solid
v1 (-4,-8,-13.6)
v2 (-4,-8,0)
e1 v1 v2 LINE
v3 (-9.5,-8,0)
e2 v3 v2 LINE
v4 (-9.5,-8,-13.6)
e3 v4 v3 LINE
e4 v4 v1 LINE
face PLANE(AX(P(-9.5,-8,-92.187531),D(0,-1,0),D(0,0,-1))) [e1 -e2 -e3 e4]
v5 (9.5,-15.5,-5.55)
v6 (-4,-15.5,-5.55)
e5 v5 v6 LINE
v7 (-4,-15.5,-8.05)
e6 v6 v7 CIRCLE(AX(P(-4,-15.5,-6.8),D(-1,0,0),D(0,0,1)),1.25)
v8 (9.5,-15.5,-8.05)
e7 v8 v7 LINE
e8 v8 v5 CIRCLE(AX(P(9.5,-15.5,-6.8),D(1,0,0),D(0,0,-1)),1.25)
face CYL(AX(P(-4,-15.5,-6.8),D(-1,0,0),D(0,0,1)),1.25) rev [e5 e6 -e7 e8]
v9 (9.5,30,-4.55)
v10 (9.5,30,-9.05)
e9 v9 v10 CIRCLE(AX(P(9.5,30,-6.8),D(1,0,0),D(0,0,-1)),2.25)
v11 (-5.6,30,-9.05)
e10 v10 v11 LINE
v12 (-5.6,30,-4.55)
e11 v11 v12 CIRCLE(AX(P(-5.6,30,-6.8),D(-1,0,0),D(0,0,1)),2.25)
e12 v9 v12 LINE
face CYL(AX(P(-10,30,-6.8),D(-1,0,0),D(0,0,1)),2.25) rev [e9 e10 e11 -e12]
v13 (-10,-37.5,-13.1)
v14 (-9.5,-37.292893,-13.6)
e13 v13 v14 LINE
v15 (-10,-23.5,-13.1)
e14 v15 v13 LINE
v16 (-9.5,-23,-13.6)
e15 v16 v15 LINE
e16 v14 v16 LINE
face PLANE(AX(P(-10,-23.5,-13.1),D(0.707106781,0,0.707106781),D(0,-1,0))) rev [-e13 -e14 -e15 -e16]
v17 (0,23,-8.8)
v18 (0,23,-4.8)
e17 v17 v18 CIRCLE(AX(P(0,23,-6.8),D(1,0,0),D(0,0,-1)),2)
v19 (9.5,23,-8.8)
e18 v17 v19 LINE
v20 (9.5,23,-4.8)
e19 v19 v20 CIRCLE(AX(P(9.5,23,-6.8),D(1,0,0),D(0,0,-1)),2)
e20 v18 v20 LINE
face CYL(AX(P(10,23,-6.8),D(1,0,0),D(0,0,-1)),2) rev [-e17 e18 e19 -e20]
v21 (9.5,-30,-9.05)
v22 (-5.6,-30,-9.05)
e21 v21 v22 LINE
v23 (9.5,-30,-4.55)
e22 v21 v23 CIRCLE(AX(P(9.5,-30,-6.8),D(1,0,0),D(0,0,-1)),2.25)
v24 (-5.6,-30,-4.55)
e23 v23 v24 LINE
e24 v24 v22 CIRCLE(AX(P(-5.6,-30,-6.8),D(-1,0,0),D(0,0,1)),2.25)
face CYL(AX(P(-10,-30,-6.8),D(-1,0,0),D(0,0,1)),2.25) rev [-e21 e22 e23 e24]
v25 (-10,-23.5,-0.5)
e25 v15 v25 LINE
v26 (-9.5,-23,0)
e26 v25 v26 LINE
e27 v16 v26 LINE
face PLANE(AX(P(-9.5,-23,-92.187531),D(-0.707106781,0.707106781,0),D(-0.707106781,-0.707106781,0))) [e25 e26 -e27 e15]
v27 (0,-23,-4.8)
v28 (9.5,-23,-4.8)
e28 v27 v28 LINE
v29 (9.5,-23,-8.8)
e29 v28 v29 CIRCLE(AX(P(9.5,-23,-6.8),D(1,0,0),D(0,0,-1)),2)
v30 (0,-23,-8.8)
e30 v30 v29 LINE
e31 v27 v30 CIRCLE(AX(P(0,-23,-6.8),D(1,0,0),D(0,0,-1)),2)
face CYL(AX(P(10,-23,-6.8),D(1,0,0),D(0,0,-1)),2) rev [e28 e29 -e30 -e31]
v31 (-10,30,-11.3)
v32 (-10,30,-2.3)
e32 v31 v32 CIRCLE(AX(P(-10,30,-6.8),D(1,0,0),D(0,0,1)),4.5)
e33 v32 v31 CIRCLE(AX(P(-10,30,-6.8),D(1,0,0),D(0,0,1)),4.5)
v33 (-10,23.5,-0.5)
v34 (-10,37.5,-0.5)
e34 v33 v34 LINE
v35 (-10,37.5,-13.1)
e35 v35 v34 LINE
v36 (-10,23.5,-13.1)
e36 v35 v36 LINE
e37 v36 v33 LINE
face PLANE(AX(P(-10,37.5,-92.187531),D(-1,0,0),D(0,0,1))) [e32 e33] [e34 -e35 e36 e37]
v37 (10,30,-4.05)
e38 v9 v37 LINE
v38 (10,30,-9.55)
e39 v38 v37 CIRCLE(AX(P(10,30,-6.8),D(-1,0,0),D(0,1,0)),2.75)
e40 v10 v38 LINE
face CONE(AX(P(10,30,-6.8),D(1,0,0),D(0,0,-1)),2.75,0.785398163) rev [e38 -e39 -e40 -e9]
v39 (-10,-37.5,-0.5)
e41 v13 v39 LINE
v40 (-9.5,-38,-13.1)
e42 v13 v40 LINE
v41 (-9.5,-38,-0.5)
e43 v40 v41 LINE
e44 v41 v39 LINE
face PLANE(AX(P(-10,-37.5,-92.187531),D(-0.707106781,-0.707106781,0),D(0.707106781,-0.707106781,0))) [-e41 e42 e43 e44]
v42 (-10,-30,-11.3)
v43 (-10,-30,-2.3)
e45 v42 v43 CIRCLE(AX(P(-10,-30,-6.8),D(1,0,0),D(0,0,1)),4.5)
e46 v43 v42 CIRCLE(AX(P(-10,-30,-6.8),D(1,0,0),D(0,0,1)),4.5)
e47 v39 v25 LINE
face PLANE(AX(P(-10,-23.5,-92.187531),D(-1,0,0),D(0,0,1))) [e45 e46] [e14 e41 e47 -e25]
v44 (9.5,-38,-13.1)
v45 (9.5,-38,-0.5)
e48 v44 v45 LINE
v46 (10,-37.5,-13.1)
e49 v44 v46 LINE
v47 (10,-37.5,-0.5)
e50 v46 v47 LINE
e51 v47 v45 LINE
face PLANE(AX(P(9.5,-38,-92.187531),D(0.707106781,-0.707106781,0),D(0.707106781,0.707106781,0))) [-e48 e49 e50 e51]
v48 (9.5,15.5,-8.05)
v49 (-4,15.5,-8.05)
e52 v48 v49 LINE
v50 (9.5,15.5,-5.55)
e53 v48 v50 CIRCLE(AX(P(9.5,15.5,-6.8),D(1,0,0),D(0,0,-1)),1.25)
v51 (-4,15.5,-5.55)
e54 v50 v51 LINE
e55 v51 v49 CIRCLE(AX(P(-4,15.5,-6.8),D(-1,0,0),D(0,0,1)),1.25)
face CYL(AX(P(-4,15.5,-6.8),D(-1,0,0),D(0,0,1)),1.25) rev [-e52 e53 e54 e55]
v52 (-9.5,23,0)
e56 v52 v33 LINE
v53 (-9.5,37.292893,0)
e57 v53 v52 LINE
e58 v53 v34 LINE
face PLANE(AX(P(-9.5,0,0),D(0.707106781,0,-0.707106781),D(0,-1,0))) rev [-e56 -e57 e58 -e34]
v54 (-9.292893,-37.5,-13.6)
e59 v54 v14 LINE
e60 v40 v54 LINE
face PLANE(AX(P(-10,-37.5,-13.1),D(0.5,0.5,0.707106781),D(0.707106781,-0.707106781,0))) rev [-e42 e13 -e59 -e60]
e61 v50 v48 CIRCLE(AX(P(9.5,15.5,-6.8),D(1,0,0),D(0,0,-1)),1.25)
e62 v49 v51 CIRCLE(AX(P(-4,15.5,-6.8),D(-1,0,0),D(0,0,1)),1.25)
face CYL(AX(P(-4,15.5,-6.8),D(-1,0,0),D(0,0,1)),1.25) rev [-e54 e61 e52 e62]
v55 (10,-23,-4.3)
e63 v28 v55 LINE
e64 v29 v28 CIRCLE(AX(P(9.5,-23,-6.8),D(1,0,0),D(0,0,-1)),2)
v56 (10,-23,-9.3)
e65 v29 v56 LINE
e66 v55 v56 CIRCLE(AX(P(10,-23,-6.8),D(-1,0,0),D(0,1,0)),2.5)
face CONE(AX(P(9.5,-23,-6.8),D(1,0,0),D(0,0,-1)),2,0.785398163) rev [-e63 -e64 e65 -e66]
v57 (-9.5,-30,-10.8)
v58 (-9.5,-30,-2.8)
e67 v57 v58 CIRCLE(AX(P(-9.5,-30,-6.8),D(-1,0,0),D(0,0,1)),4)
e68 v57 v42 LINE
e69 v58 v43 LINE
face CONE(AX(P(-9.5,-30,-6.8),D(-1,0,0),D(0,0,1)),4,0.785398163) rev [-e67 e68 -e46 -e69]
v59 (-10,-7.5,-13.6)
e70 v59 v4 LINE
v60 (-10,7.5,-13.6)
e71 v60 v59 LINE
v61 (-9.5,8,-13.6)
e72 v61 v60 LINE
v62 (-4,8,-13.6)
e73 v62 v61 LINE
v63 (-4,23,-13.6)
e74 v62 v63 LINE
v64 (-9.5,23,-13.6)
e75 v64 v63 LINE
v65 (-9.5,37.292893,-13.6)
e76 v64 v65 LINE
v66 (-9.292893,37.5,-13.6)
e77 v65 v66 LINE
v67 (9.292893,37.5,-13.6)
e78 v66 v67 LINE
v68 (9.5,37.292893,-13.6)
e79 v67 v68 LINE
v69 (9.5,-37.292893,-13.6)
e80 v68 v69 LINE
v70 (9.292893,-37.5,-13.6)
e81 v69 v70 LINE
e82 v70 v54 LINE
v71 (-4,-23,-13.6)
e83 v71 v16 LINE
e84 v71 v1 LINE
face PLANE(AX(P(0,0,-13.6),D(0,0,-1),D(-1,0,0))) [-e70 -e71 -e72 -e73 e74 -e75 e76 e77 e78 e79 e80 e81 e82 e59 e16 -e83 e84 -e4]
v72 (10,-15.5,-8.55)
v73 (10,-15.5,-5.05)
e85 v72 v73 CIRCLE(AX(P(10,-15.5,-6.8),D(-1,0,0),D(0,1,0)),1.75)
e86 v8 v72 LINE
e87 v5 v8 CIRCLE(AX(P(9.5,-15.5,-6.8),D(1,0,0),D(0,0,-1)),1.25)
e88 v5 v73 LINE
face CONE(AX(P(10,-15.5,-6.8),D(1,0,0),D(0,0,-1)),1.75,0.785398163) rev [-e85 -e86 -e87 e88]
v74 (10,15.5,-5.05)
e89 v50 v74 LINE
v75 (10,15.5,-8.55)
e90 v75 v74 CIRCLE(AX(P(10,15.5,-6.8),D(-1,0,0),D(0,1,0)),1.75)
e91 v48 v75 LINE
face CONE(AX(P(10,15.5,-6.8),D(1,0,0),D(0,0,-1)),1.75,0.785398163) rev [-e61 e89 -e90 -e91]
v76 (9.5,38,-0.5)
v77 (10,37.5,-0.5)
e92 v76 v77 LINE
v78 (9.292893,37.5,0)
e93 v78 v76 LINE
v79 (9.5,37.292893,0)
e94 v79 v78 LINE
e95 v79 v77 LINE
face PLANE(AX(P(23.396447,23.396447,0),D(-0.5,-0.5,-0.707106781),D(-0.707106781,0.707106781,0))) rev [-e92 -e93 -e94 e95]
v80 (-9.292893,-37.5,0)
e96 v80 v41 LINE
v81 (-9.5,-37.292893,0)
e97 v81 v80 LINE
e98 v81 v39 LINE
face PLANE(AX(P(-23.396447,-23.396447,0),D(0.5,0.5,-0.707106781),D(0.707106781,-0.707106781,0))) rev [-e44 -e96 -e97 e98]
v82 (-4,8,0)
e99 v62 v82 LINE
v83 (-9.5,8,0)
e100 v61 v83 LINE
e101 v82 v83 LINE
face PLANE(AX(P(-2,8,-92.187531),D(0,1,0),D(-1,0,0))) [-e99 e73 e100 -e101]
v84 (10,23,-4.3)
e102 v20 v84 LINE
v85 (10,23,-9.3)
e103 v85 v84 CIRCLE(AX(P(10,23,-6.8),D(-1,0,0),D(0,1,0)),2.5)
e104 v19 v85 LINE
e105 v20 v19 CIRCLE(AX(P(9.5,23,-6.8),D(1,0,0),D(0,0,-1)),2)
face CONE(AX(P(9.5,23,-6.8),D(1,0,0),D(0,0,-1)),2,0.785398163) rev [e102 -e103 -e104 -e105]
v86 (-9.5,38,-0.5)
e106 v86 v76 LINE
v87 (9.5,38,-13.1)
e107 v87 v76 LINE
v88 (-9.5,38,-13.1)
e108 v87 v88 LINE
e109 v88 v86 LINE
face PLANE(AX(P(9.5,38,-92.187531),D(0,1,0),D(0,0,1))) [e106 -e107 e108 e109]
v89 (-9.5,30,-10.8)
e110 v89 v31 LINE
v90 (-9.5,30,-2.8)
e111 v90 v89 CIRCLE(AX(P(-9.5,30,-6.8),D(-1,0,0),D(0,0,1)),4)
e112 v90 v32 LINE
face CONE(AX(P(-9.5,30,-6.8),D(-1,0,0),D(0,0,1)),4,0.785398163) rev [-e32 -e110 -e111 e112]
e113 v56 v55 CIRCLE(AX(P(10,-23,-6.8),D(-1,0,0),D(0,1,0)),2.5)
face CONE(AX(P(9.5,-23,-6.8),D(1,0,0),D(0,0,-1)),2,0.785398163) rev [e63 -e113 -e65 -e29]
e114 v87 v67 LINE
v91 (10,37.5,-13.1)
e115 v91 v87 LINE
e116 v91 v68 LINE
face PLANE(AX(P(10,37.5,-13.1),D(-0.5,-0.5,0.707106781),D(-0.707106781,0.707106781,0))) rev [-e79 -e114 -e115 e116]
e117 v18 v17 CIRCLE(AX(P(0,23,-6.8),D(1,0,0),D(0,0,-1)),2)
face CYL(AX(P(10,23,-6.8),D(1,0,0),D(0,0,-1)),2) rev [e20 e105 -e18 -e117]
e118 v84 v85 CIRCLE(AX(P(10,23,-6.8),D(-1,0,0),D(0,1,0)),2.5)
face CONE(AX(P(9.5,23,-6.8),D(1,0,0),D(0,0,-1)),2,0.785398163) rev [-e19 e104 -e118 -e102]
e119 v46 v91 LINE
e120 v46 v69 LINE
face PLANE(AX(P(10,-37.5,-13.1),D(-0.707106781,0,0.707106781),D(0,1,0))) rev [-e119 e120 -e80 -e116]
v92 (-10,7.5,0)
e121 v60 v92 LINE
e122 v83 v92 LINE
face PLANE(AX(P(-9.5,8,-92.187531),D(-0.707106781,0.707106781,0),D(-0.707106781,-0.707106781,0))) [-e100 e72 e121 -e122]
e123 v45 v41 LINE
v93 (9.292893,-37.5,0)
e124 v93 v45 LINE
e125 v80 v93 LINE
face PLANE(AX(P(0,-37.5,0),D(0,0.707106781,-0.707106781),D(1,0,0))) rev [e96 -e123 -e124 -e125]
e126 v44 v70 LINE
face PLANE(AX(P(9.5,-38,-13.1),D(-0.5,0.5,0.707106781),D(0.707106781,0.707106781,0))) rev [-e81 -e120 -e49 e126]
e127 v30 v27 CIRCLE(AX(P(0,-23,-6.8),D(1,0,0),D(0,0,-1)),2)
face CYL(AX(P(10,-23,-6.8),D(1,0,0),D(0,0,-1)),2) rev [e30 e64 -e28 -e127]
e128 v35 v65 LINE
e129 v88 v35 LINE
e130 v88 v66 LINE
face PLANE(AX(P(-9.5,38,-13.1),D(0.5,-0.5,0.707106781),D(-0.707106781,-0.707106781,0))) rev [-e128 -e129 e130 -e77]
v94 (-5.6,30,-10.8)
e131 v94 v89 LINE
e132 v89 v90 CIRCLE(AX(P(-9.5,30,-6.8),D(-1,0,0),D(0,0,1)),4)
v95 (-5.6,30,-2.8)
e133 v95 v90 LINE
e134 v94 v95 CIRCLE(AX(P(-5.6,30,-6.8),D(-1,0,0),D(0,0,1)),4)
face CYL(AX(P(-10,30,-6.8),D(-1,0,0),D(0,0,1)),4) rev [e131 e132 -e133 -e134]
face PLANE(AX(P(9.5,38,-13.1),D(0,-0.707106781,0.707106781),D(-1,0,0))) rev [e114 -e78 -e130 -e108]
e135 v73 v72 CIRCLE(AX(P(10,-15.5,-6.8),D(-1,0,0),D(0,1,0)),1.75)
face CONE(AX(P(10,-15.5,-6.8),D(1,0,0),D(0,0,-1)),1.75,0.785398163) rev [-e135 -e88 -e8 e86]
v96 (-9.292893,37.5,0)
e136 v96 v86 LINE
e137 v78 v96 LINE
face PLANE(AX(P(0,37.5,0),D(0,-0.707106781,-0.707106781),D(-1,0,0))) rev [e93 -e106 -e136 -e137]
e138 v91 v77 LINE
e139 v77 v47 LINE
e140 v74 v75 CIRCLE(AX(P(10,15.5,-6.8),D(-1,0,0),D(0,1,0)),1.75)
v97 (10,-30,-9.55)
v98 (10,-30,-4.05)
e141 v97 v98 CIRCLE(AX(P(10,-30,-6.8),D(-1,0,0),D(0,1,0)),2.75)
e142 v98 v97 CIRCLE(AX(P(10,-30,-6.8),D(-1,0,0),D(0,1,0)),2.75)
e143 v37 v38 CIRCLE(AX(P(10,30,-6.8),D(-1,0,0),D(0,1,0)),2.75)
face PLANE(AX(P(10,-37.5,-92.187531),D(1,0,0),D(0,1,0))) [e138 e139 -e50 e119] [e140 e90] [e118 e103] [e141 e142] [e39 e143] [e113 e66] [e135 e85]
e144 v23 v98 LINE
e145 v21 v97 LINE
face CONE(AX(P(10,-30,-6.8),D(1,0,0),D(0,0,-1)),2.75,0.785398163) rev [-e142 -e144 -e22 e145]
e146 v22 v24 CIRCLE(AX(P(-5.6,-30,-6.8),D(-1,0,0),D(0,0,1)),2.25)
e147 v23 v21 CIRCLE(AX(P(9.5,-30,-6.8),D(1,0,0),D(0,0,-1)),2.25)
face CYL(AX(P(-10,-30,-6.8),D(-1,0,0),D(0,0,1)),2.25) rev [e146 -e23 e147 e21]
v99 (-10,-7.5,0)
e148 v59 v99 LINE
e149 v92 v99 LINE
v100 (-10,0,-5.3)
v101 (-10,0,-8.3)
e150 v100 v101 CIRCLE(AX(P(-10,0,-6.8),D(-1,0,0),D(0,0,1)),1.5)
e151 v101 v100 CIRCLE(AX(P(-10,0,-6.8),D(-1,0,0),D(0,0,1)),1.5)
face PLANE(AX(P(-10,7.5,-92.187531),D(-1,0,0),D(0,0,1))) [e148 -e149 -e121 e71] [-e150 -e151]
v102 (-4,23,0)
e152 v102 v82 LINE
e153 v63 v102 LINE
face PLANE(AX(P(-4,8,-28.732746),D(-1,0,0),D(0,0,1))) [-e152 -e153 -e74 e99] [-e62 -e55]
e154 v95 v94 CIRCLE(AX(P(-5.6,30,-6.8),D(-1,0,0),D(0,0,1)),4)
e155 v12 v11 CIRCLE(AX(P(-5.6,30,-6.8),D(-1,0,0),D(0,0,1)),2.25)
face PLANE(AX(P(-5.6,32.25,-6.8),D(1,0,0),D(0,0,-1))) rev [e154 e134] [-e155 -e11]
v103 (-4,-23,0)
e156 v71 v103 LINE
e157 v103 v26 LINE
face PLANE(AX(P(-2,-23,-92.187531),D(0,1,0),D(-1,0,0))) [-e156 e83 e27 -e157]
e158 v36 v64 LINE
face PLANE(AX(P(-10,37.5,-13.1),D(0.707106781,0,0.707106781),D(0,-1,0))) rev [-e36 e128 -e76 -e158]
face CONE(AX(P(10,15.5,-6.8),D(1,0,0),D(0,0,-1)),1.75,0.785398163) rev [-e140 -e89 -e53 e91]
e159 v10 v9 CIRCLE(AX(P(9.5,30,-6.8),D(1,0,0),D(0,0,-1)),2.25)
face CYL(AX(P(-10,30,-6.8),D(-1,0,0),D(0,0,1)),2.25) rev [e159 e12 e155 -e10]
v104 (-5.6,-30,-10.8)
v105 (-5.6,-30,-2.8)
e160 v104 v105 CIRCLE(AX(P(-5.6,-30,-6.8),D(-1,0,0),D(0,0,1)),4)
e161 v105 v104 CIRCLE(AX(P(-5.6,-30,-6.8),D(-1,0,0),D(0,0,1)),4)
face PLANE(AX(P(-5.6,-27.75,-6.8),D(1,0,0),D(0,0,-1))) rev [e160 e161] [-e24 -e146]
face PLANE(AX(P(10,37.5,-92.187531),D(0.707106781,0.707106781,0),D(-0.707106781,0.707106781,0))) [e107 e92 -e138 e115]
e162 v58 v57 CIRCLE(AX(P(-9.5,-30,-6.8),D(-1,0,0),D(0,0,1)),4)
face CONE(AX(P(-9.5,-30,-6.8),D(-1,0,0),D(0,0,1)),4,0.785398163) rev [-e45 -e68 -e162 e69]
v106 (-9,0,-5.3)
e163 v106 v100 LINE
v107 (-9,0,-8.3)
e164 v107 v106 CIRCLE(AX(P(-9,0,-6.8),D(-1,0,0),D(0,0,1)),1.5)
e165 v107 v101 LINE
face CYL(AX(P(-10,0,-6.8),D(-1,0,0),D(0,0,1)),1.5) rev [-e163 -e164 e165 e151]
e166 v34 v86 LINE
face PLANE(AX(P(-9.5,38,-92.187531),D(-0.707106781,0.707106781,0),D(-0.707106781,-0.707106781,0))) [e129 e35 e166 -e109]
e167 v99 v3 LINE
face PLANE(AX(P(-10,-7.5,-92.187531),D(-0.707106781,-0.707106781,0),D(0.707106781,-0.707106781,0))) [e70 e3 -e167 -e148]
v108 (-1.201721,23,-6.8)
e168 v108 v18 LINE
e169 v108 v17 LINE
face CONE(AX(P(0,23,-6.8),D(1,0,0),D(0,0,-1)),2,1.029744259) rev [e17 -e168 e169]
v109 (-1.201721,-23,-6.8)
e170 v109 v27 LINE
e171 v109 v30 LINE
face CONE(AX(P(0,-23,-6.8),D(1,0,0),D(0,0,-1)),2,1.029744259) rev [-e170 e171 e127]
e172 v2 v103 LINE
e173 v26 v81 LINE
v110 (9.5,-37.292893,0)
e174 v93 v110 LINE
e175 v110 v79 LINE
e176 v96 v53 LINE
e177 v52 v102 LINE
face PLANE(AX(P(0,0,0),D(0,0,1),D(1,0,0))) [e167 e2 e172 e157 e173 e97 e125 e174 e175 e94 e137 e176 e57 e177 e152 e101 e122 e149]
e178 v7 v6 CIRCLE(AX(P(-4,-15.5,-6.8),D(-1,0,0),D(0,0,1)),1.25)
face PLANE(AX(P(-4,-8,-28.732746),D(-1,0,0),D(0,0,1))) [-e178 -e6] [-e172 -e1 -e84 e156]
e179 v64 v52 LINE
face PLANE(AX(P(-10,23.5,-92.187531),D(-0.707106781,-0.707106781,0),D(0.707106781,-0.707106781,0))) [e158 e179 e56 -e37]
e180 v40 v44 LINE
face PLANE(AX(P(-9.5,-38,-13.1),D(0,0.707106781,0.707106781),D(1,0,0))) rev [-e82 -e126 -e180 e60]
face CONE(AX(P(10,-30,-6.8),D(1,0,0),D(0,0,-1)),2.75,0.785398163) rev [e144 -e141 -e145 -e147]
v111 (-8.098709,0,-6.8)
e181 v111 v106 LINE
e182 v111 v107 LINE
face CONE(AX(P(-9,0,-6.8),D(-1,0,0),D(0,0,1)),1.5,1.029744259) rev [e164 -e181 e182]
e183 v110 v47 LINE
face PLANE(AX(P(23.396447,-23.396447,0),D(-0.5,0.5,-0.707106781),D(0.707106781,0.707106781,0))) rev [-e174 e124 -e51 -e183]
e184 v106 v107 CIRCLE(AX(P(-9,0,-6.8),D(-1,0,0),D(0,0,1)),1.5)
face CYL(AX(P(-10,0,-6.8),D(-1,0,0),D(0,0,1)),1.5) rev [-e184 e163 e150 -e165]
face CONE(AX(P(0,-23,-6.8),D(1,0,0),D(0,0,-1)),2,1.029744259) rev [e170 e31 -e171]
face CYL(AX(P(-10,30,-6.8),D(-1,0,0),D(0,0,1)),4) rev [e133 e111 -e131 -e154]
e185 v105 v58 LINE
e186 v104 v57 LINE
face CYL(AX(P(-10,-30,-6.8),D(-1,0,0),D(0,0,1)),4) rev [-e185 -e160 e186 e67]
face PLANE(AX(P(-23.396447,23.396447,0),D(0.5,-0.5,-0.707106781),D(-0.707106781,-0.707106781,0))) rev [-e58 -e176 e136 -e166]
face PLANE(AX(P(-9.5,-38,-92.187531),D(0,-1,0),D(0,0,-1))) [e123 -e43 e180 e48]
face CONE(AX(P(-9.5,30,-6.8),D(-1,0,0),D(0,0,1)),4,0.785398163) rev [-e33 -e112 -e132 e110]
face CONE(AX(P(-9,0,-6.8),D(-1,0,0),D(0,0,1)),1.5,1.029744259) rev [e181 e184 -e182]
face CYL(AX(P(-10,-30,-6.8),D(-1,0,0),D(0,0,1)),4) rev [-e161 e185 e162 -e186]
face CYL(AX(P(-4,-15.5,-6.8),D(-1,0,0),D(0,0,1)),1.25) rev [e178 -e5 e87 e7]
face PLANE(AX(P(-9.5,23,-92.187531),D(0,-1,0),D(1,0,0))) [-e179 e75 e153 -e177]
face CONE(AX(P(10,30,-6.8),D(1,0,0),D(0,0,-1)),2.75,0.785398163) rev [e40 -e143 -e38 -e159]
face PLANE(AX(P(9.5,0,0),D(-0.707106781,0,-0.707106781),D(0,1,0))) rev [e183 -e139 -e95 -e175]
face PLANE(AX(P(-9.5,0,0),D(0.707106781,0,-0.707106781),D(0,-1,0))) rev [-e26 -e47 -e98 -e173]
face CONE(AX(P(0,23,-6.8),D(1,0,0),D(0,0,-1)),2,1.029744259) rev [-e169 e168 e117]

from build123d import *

# Parameters (mm, degrees)
EXTRUDE_1_DEPTH              = 13.6
CHAMFER_1_SIZE               = 0.5
HOLE_WIZARD_M4_1_D           = 4.5
HOLE_WIZARD_M4_1_CBORE_D     = 8
HOLE_WIZARD_M4_1_CBORE_DEPTH = 4.4
SKETCH_6_W                   = 2
SKETCH_6_H                   = 15
EXTRUDE_2_DEPTH              = 13.6
HOLE_WIZARD_M3_1_D           = 2.5
MM_1_D                       = 4
MM_1_DEPTH                   = 10
MM_1_TIP                     = 1.201721238
CHAMFER_2_SIZE               = 0.5
MM_2_D                       = 3
MM_2_DEPTH                   = 1
MM_2_TIP                     = 0.901290929


with BuildPart() as part:
    # 草图3 → 凸台-拉伸1 (new body)
    with BuildSketch(Plane.XY):
        Polygon((10, 37.5), (9.5, 38), (-9.5, 38), (-10, 37.5), (-10, 23.5), (-9.5, 23), (-2, 23), (-2, 8), (-9.5, 8), (-10, 7.5), (-10, -7.5), (-9.5, -8), (-2, -8), (-2, -23), (-9.5, -23), (-10, -23.5), (-10, -37.5), (-9.5, -38), (9.5, -38), (10, -37.5), align=None)
    extrude(amount=-EXTRUDE_1_DEPTH)

    # 倒角1
    chamfer_1_edges = [part.edges().sort_by_distance(p)[0] for p in [
        (-10, 30.5, -13.6),
        (-9.75, 37.75, -13.6),
        (0, 38, -13.6),
        (9.75, 37.75, -13.6),
        (10, 0, -13.6),
        (9.75, -37.75, -13.6),
        (-10, -30.5, -13.6),
        (-9.75, -37.75, -13.6),
        (0, -38, -13.6),
        (-10, 30.5, 0),
        (-9.75, 37.75, 0),
        (0, 38, 0),
        (9.75, 37.75, 0),
        (10, 0, 0),
        (9.75, -37.75, 0),
        (-10, -30.5, 0),
        (-9.75, -37.75, 0),
        (0, -38, 0),
    ]]
    chamfer(chamfer_1_edges, length=CHAMFER_1_SIZE)

    # M4 六角凹头螺钉的柱形沉头孔1 (through all)
    with Locations(Plane.ZY.offset(10)):
        with Locations((-6.8, -30), (-6.8, 30)):
            CounterBoreHole(HOLE_WIZARD_M4_1_D / 2, HOLE_WIZARD_M4_1_CBORE_D / 2, HOLE_WIZARD_M4_1_CBORE_DEPTH)

    # 草图6 → 凸台-拉伸2 (add)
    with BuildSketch(Plane.XY):
        with Locations((-3, -15.5)):
            Rectangle(SKETCH_6_W, SKETCH_6_H)
        with Locations((-3, 15.5)):
            Rectangle(SKETCH_6_W, SKETCH_6_H)
    extrude(amount=-EXTRUDE_2_DEPTH)

    # M3 螺纹孔1 (through all)
    with Locations(Plane.ZY.offset(4)):
        with Locations((-6.8, -15.5), (-6.8, 15.5)):
            Hole(HOLE_WIZARD_M3_1_D / 2)

    # 大小mm 暗销孔1
    with Locations(Plane(origin=(10, 0, 0), x_dir=(0, 0, -1), z_dir=(1, 0, 0))):
        with Locations((6.8, -23), (6.8, 23)):
            Hole(MM_1_D / 2, depth=MM_1_DEPTH)
            with Locations((0, 0, -(MM_1_DEPTH + MM_1_TIP / 2))):  # 118° drill point
                Cone(0, MM_1_D / 2, MM_1_TIP, mode=Mode.SUBTRACT)

    # 倒角2
    chamfer_2_edges = [part.edges().sort_by_distance(p)[0] for p in [
        (-10, 30, -10.8),
        (10, 30, -4.55),
        (-10, -30, -10.8),
        (10, -30, -4.55),
        (10, 15.5, -5.55),
        (10, -15.5, -5.55),
        (10, 23, -8.8),
        (10, -23, -8.8),
    ]]
    chamfer(chamfer_2_edges, length=CHAMFER_2_SIZE)

    # 大小mm 暗销孔2
    with Locations(Plane.ZY.offset(10)):
        with Locations((-6.8, 0)):
            Hole(MM_2_D / 2, depth=MM_2_DEPTH)
            with Locations((0, 0, -(MM_2_DEPTH + MM_2_TIP / 2))):  # 118° drill point
                Cone(0, MM_2_D / 2, MM_2_TIP, mode=Mode.SUBTRACT)


solid = part.part
